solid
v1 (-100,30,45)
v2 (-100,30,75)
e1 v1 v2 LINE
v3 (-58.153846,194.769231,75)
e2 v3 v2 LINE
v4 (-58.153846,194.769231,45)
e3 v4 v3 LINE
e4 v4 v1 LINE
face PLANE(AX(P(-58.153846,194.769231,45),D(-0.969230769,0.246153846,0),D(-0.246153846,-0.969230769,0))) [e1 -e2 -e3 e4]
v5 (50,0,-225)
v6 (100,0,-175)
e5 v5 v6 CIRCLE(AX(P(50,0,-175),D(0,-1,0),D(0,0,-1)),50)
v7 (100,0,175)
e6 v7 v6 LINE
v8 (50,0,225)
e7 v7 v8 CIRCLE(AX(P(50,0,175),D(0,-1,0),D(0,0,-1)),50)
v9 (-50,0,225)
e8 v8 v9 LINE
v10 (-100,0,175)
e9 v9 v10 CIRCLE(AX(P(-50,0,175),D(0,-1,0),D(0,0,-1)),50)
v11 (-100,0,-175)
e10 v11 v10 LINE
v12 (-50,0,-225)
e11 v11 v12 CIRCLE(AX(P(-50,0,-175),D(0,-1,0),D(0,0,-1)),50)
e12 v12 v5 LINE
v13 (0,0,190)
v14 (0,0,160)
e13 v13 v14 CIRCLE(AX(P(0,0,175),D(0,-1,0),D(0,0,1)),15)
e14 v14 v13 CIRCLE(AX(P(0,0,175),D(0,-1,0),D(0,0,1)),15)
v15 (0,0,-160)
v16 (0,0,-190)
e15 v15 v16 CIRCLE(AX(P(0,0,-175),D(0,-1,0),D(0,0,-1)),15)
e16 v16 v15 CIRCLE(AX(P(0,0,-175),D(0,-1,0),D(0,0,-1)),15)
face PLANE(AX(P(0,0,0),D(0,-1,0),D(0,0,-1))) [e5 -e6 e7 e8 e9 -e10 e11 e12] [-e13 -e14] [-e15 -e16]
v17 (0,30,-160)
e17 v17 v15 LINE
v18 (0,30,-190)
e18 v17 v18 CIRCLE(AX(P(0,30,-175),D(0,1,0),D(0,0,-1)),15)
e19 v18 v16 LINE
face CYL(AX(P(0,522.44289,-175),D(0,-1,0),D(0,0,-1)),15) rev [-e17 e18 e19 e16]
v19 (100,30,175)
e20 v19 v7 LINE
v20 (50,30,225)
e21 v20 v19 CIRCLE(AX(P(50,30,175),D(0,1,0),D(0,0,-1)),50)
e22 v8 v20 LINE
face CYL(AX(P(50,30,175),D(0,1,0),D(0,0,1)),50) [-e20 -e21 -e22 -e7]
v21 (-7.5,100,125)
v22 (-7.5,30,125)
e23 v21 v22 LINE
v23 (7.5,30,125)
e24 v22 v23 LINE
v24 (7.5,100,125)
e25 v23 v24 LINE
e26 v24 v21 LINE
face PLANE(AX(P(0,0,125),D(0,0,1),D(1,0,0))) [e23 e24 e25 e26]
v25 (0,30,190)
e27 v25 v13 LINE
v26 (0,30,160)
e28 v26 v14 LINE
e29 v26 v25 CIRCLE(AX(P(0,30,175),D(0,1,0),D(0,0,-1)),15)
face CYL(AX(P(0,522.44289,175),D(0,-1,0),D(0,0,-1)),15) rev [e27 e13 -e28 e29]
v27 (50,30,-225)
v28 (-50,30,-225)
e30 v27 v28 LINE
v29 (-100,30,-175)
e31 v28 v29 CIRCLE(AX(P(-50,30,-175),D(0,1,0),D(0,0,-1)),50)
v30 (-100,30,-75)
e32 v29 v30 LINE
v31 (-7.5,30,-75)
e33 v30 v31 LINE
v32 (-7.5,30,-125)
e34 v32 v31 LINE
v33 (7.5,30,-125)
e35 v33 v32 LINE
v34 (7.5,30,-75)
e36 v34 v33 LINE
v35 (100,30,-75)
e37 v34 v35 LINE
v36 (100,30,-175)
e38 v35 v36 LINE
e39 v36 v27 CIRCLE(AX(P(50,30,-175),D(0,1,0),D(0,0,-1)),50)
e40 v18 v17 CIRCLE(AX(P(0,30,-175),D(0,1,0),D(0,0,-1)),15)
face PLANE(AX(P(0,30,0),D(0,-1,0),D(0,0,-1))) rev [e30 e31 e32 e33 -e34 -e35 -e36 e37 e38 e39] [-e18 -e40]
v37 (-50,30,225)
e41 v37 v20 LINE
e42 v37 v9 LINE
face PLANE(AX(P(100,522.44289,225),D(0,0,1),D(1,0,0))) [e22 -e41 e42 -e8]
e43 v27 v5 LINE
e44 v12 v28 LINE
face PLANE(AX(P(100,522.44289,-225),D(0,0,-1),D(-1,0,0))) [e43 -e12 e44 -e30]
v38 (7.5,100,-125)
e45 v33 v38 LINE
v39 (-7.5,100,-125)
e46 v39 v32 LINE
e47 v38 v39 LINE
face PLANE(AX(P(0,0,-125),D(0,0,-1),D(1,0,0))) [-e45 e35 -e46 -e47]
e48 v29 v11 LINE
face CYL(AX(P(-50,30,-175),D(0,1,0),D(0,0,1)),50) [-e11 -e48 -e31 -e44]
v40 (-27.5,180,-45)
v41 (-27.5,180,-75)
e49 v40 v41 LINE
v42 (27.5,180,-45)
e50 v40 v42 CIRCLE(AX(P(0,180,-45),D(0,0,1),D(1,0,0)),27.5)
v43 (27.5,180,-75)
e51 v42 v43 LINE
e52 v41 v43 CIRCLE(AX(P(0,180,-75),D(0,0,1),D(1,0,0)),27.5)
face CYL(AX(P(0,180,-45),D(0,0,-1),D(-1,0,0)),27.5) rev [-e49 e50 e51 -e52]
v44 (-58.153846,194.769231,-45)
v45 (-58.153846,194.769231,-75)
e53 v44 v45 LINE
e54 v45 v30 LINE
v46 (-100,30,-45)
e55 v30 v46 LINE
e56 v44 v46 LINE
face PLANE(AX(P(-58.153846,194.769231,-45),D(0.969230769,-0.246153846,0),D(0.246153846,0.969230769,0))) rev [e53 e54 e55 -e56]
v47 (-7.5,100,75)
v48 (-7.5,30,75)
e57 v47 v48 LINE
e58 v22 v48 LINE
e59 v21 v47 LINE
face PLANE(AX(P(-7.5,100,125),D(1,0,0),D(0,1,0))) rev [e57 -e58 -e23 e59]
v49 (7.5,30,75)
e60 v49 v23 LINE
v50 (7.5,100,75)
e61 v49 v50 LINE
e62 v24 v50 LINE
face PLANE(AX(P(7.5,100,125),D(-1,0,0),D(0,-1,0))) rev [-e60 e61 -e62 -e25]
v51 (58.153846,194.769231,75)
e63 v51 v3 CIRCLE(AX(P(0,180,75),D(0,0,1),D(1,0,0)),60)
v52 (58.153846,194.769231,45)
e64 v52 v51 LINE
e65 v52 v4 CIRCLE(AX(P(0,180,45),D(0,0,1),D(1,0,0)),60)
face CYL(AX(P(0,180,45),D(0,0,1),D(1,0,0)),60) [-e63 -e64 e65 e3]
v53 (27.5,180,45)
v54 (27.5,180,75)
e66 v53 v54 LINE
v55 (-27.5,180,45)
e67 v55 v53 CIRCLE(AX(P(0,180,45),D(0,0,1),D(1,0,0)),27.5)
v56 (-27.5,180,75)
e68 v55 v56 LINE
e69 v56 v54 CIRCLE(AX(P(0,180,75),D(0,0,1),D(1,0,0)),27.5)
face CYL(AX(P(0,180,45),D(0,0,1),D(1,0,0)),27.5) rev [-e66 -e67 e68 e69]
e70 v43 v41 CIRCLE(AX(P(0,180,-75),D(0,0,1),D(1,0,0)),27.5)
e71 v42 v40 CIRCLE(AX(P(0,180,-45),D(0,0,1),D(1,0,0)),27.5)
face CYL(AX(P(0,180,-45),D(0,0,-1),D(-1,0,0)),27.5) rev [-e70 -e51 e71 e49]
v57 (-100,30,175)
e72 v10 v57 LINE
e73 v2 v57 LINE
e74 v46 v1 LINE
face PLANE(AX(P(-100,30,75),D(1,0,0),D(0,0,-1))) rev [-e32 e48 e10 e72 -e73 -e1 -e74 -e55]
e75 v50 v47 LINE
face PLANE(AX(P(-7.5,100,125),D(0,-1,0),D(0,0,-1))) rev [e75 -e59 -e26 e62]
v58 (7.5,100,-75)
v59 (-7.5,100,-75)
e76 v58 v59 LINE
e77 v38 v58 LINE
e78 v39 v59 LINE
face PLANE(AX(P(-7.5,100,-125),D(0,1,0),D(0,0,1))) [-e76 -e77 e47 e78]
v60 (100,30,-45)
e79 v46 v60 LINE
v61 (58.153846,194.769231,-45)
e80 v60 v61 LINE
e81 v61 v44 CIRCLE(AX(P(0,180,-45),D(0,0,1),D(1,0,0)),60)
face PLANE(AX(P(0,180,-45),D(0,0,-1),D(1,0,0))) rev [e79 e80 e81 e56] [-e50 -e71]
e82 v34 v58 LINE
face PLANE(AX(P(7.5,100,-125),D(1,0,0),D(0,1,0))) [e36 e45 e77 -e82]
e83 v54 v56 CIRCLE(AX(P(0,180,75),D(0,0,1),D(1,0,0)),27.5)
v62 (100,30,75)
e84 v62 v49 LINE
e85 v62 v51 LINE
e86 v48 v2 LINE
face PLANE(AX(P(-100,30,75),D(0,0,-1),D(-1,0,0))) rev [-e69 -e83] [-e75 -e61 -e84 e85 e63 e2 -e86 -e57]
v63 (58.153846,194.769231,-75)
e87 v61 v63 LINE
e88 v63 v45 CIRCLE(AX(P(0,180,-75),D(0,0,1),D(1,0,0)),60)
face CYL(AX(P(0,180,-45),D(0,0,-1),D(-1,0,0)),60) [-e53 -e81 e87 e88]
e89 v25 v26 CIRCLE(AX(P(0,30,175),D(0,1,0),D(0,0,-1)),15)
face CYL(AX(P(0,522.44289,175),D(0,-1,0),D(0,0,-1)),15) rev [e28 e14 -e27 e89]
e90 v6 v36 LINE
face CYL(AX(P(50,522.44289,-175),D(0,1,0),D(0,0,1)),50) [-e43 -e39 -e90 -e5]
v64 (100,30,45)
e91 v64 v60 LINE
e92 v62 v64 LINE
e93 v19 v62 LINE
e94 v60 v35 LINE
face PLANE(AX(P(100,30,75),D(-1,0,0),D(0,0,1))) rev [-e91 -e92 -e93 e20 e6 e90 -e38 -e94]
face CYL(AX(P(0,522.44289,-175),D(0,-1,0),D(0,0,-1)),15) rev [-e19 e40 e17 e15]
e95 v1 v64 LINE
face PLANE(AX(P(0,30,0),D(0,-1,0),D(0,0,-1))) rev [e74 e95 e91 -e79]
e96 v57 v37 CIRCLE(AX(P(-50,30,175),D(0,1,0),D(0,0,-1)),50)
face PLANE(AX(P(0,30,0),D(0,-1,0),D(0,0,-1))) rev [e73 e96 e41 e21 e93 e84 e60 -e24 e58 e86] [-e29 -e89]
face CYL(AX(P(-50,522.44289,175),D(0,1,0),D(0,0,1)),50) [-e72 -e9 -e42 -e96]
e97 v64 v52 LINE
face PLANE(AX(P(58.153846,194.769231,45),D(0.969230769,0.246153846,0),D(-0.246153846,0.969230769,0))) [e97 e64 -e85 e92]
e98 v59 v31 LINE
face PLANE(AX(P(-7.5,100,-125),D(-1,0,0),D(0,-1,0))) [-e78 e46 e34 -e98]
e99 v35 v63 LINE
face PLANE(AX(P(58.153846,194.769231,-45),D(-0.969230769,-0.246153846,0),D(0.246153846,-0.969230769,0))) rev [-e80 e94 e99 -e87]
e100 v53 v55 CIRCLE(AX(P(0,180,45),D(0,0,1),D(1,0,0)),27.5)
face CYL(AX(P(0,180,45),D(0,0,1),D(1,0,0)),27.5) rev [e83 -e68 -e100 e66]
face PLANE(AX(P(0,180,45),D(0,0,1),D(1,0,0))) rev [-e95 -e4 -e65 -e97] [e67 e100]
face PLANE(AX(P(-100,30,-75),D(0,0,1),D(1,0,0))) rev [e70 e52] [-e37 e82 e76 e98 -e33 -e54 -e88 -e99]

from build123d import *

# Parameters (mm, degrees)
SKETCH_1_W           = 200
SKETCH_1_H           = 150
BOSS_EXTRUDE_1_DEPTH = 30
SKETCH_2_R           = 27.5
BOSS_EXTRUDE_2_DEPTH = 30
SKETCH_4_W           = 15
SKETCH_4_H           = 100
BOSS_EXTRUDE_3_DEPTH = 50
SKETCH_5_W           = 200
SKETCH_5_H           = 450
SKETCH_5_R           = 15
BOSS_EXTRUDE_4_DEPTH = 30
FILLET_1_R           = 50


with BuildPart() as part:
    # Sketch 1 → Boss-Extrude 1 (new body)
    with BuildSketch(Plane(origin=(0, 0, 0), x_dir=(1, 0, 0), z_dir=(0, 1, 0))):
        Rectangle(SKETCH_1_W, SKETCH_1_H)
    extrude(amount=BOSS_EXTRUDE_1_DEPTH)

    # Sketch 2 → Boss-Extrude 2 (add)
    with BuildSketch(Plane.XY.offset(75)):
        with BuildLine():
            Line((-58.153846154, 194.769230769), (-100, 30))
            Line((-100, 30), (100, 30))
            Line((100, 30), (58.153846154, 194.769230769))
            ThreePointArc((58.153846154, 194.769230769), (0, 240), (-58.153846154, 194.769230769))
        make_face()
        with Locations((0, 180)):
            Circle(SKETCH_2_R, mode=Mode.SUBTRACT)
    boss_extrude_2 = extrude(amount=-BOSS_EXTRUDE_2_DEPTH)

    # Sketch 4 → Boss-Extrude 3 (add)
    with BuildSketch(Plane.XY.offset(75)):
        with Locations((0, 50)):
            Rectangle(SKETCH_4_W, SKETCH_4_H)
    boss_extrude_3 = extrude(amount=BOSS_EXTRUDE_3_DEPTH)

    # Mirror 1: Boss-Extrude 2, Boss-Extrude 3 across plane
    add(boss_extrude_2.mirror(Plane.XY))
    add(boss_extrude_3.mirror(Plane.XY))

    # Sketch 5 → Boss-Extrude 4 (add)
    with BuildSketch(Plane.XZ):
        Rectangle(SKETCH_5_W, SKETCH_5_H)
        with Locations(Location((0, -175, 0), (0, 0, 270))):
            Circle(SKETCH_5_R, mode=Mode.SUBTRACT)
        with Locations(Location((0, 175, 0), (0, 0, 270))):
            Circle(SKETCH_5_R, mode=Mode.SUBTRACT)
    extrude(amount=-BOSS_EXTRUDE_4_DEPTH)

    # Fillet 1
    fillet_1_edges = [part.edges().sort_by_distance(p)[0] for p in [
        (-100, 15, -225),
        (100, 15, 225),
        (100, 15, -225),
        (-100, 15, 225),
    ]]
    fillet(fillet_1_edges, radius=FILLET_1_R)


solid = part.part
